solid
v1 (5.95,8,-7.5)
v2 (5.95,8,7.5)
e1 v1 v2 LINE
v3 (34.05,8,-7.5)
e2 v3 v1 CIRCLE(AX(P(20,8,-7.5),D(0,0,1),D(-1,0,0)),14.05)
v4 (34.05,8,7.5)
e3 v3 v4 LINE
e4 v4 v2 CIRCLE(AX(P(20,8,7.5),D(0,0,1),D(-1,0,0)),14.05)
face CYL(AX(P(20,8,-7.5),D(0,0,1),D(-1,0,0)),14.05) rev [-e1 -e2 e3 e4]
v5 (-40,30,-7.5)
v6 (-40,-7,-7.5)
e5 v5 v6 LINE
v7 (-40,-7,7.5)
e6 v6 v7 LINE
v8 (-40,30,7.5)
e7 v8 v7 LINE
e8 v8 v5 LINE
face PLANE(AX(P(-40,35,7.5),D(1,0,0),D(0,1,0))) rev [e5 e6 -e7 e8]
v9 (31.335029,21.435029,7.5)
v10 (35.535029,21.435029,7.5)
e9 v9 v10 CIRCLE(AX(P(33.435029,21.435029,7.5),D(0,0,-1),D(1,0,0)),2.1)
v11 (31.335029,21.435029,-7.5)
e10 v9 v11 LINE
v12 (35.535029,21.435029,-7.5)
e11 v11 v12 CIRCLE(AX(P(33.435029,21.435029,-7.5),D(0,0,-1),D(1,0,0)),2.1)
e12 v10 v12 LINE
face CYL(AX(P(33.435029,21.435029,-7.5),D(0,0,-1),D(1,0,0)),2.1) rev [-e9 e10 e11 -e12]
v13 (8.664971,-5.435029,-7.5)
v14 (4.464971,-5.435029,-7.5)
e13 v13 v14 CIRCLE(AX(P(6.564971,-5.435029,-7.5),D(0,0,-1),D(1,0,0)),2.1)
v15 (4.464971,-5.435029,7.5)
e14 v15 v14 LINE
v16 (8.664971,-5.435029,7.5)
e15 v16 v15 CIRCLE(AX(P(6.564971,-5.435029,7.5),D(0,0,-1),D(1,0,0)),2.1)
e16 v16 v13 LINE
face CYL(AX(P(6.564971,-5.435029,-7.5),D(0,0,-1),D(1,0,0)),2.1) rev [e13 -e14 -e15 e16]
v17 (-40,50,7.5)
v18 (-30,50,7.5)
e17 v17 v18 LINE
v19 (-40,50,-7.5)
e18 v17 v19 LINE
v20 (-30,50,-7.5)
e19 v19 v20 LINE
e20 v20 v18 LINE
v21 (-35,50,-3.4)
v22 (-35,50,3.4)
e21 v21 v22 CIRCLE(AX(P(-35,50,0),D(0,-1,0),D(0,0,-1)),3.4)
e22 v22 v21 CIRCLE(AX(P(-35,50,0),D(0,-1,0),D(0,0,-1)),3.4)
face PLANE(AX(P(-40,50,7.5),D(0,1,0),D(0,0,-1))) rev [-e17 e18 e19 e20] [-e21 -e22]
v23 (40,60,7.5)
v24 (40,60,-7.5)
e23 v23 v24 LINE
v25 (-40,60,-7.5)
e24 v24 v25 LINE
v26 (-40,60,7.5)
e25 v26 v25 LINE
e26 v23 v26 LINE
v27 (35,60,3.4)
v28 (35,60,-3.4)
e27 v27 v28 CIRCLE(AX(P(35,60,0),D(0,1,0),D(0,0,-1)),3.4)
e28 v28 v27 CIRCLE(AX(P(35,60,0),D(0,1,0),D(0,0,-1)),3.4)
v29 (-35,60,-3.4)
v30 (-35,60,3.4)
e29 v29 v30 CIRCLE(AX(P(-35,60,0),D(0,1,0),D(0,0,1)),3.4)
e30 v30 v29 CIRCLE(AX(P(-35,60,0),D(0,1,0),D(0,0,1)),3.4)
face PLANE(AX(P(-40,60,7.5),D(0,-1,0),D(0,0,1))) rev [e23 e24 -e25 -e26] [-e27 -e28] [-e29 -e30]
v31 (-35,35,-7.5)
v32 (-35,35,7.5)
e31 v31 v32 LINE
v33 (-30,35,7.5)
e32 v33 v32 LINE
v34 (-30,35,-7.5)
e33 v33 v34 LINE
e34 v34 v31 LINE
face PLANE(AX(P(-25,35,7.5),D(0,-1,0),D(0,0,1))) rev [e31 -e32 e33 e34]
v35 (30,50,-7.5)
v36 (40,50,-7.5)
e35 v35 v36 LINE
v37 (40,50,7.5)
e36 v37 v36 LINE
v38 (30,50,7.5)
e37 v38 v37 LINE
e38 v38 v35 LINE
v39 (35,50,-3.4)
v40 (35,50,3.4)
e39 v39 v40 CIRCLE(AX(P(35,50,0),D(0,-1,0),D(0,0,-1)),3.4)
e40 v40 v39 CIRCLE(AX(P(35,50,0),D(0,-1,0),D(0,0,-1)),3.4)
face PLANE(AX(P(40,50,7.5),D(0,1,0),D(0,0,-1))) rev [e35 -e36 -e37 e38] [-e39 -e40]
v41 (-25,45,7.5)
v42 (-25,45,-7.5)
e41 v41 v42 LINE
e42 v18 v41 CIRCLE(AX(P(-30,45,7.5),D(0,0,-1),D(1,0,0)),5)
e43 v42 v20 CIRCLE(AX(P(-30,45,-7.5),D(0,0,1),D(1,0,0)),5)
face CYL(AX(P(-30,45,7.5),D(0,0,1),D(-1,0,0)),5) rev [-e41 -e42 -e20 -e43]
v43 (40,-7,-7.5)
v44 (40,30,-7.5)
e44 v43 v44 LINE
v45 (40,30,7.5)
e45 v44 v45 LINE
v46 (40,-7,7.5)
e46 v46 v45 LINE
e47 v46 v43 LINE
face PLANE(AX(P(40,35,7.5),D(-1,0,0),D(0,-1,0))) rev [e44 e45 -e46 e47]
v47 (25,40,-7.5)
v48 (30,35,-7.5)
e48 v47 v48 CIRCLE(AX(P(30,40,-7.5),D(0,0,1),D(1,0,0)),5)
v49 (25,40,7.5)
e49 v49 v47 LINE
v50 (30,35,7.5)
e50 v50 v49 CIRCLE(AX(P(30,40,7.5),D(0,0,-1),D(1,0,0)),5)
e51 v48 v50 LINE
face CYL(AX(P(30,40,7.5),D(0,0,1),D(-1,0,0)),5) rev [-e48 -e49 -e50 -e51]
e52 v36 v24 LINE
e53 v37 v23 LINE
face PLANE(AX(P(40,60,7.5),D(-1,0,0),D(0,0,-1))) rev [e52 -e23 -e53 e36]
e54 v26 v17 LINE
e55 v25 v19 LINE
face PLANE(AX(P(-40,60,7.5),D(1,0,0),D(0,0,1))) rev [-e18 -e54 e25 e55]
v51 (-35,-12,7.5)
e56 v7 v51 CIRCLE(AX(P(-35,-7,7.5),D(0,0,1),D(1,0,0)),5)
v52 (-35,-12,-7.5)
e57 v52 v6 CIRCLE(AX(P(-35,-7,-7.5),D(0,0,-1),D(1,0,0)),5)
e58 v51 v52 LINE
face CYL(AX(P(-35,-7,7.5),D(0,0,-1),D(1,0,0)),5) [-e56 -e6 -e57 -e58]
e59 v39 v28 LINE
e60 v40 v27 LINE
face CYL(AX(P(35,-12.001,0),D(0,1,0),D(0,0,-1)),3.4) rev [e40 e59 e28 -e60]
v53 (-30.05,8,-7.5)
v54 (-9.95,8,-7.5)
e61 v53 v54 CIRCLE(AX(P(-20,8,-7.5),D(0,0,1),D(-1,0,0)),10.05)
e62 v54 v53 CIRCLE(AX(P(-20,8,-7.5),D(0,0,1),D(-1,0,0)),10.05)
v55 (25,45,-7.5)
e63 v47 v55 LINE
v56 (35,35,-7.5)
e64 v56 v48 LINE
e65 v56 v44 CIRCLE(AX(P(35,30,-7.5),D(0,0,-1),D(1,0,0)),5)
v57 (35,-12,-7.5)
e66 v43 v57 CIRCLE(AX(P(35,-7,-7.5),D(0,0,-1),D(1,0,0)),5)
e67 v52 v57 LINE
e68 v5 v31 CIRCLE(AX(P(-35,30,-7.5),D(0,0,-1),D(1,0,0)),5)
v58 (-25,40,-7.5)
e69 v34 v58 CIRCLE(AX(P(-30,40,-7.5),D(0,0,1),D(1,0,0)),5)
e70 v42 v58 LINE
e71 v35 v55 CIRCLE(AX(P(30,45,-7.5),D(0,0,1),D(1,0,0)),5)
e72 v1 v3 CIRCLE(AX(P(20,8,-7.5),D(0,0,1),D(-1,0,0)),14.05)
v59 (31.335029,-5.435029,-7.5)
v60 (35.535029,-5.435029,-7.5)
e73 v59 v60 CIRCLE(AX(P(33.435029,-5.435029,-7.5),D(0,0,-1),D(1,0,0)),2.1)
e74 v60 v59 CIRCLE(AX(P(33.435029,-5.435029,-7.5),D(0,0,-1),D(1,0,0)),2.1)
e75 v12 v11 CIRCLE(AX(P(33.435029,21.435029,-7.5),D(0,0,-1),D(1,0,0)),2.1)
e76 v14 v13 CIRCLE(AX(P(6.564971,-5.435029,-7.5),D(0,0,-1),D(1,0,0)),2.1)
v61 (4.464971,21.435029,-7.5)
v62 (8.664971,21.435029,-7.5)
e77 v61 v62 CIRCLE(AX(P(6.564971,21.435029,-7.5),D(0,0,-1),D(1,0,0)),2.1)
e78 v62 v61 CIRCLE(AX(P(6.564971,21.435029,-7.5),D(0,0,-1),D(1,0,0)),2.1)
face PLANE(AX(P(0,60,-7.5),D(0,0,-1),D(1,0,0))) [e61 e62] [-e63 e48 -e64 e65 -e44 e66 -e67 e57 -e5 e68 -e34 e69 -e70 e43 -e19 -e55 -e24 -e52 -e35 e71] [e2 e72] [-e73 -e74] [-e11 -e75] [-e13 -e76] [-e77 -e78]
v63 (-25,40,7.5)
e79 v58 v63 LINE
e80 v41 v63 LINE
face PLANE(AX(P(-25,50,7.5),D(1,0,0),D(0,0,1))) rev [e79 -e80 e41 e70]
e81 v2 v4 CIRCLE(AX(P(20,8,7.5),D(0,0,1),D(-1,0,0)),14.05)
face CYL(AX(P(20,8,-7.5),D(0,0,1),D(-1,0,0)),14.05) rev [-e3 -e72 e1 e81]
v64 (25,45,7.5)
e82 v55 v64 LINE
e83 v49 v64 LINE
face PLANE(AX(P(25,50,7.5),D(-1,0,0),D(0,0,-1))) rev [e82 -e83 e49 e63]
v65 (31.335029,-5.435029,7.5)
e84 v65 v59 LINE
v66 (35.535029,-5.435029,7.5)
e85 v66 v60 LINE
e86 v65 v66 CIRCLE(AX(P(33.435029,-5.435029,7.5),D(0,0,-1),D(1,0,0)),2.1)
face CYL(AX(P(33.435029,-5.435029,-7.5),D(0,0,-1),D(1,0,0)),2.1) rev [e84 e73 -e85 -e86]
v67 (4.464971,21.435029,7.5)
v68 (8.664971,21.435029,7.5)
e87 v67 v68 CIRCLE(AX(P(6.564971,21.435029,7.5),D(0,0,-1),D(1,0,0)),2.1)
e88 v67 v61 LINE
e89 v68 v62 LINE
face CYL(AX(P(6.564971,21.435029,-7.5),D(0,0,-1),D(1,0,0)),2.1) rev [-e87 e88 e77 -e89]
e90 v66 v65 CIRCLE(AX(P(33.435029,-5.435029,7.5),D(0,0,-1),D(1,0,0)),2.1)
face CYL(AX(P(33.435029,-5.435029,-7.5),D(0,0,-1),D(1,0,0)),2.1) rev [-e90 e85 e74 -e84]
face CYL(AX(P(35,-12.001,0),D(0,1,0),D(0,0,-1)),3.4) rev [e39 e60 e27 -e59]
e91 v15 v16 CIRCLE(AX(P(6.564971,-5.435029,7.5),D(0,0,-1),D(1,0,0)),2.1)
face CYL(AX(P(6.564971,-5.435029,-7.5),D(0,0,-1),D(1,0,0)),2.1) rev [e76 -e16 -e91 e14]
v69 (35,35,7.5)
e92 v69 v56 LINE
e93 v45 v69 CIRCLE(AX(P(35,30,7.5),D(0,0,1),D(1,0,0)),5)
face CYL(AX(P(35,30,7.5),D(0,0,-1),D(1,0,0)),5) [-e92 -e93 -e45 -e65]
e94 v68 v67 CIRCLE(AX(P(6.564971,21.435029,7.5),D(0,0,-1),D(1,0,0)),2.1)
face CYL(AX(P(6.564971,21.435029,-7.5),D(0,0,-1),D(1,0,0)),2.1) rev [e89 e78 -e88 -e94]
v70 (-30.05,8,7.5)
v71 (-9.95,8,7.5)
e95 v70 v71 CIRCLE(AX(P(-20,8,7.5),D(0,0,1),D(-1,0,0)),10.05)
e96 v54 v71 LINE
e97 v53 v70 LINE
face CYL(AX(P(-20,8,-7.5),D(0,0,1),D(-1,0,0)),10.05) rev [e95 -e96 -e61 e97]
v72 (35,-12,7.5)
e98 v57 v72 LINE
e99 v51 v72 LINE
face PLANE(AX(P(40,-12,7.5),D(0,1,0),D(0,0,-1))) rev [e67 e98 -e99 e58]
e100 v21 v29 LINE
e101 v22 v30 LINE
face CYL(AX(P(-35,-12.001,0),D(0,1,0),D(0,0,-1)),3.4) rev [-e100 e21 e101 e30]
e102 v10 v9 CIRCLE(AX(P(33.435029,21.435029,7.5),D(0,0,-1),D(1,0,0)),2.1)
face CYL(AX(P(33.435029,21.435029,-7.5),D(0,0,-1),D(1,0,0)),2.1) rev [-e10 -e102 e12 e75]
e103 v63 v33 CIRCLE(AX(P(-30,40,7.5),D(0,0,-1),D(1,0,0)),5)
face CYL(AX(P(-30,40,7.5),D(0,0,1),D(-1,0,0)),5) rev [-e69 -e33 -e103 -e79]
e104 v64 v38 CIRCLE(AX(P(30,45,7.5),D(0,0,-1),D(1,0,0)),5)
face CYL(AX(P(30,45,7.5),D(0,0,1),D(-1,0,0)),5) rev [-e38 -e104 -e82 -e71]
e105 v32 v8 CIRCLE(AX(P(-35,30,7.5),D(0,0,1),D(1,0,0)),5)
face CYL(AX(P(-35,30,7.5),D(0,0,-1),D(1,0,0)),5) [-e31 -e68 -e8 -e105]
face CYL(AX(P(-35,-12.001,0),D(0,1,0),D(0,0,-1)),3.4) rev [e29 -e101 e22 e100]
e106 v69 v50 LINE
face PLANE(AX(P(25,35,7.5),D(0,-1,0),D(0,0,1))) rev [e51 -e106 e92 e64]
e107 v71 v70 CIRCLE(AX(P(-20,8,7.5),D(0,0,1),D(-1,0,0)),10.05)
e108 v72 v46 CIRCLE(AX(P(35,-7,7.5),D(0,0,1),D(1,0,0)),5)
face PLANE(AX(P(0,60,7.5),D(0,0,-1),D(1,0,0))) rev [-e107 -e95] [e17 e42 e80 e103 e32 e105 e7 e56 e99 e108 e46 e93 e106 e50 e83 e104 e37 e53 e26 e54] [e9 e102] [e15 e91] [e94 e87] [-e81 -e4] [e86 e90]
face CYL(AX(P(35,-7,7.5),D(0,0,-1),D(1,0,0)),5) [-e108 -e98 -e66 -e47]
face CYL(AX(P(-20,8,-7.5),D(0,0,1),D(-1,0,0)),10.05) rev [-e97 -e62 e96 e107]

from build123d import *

# Parameters (mm, degrees)
BOSS_EXTRUDE1_DEPTH   = 7.5
CUT_EXTRUDE1_REACH    = 84.706
SKETCH2_R             = 3.4
SKETCH3_R             = 14.05
SKETCH3_R_2           = 10.05
CUT_EXTRUDE2_DEPTH    = 15
FILLET1_R             = 5
M5_TAPPED_HOLE1_D     = 4.2
BODY_MOVE_COPY1_ANGLE = 180


with BuildPart() as part:
    # Sketch1 → Boss-Extrude1 (new, symmetric)
    with BuildSketch(Plane.XY):
        Polygon((40, 0), (-40, 0), (-40, 10), (-25, 10), (-25, 25), (-40, 25), (-40, 72), (40, 72), (40, 25), (25, 25), (25, 10), (40, 10), align=None)
    extrude(amount=BOSS_EXTRUDE1_DEPTH, both=True)

    # Sketch2 → Cut-Extrude1 (cut, up to next)
    with BuildSketch(Plane.XZ, mode=Mode.PRIVATE) as cut_extrude1_sk1:
        with Locations(Location((-35, 0, 0), (0, 0, 270))):
            Circle(SKETCH2_R)
    cut_extrude1_tool1 = extrude(cut_extrude1_sk1.sketch, amount=-CUT_EXTRUDE1_REACH, mode=Mode.PRIVATE) & part.part
    # Sketch2 → Cut-Extrude1 (cut, up to next)
    with BuildSketch(Plane.XZ, mode=Mode.PRIVATE) as cut_extrude1_sk2:
        with Locations(Location((35, 0, 0), (0, 0, 270))):
            Circle(SKETCH2_R)
    cut_extrude1_tool2 = extrude(cut_extrude1_sk2.sketch, amount=-CUT_EXTRUDE1_REACH, mode=Mode.PRIVATE) & part.part
    add(cut_extrude1_tool1.solids().sort_by_distance((-35, 0, 0))[0], mode=Mode.SUBTRACT)
    add(cut_extrude1_tool2.solids().sort_by_distance((35, 0, 0))[0], mode=Mode.SUBTRACT)

    # Sketch3 → Cut-Extrude2 (cut)
    with BuildSketch(Plane.XY.offset(7.5)):
        with Locations((-20, 52)):
            Circle(SKETCH3_R)
        with Locations((20, 52)):
            Circle(SKETCH3_R_2)
    extrude(amount=-CUT_EXTRUDE2_DEPTH, mode=Mode.SUBTRACT)

    # Fillet1
    fillet1_edges = [part.edges().sort_by_distance(p)[0] for p in [
        (-25, 10, 0),
        (-25, 25, 0),
        (-40, 25, 0),
        (-40, 72, 0),
        (40, 72, 0),
        (40, 25, 0),
        (25, 25, 0),
        (25, 10, 0),
    ]]
    fillet(fillet1_edges, radius=FILLET1_R)

    # M5 Tapped Hole1 (through all)
    with Locations(Plane(origin=(0, 0, -7.5), x_dir=(-1, 0, 0), z_dir=(0, 0, -1))):
        with Locations((33.435028843, 38.564971157), (6.564971157, 38.564971157), (6.564971157, 65.435028843), (33.435028843, 65.435028843)):
            Hole(M5_TAPPED_HOLE1_D / 2)


with BuildPart() as part_1:
    # Body-Move/Copy1: moved
    add(part.part.rotate(Axis((0, 30, 0), (0, 0, 1)), BODY_MOVE_COPY1_ANGLE))


solid = part_1.part
